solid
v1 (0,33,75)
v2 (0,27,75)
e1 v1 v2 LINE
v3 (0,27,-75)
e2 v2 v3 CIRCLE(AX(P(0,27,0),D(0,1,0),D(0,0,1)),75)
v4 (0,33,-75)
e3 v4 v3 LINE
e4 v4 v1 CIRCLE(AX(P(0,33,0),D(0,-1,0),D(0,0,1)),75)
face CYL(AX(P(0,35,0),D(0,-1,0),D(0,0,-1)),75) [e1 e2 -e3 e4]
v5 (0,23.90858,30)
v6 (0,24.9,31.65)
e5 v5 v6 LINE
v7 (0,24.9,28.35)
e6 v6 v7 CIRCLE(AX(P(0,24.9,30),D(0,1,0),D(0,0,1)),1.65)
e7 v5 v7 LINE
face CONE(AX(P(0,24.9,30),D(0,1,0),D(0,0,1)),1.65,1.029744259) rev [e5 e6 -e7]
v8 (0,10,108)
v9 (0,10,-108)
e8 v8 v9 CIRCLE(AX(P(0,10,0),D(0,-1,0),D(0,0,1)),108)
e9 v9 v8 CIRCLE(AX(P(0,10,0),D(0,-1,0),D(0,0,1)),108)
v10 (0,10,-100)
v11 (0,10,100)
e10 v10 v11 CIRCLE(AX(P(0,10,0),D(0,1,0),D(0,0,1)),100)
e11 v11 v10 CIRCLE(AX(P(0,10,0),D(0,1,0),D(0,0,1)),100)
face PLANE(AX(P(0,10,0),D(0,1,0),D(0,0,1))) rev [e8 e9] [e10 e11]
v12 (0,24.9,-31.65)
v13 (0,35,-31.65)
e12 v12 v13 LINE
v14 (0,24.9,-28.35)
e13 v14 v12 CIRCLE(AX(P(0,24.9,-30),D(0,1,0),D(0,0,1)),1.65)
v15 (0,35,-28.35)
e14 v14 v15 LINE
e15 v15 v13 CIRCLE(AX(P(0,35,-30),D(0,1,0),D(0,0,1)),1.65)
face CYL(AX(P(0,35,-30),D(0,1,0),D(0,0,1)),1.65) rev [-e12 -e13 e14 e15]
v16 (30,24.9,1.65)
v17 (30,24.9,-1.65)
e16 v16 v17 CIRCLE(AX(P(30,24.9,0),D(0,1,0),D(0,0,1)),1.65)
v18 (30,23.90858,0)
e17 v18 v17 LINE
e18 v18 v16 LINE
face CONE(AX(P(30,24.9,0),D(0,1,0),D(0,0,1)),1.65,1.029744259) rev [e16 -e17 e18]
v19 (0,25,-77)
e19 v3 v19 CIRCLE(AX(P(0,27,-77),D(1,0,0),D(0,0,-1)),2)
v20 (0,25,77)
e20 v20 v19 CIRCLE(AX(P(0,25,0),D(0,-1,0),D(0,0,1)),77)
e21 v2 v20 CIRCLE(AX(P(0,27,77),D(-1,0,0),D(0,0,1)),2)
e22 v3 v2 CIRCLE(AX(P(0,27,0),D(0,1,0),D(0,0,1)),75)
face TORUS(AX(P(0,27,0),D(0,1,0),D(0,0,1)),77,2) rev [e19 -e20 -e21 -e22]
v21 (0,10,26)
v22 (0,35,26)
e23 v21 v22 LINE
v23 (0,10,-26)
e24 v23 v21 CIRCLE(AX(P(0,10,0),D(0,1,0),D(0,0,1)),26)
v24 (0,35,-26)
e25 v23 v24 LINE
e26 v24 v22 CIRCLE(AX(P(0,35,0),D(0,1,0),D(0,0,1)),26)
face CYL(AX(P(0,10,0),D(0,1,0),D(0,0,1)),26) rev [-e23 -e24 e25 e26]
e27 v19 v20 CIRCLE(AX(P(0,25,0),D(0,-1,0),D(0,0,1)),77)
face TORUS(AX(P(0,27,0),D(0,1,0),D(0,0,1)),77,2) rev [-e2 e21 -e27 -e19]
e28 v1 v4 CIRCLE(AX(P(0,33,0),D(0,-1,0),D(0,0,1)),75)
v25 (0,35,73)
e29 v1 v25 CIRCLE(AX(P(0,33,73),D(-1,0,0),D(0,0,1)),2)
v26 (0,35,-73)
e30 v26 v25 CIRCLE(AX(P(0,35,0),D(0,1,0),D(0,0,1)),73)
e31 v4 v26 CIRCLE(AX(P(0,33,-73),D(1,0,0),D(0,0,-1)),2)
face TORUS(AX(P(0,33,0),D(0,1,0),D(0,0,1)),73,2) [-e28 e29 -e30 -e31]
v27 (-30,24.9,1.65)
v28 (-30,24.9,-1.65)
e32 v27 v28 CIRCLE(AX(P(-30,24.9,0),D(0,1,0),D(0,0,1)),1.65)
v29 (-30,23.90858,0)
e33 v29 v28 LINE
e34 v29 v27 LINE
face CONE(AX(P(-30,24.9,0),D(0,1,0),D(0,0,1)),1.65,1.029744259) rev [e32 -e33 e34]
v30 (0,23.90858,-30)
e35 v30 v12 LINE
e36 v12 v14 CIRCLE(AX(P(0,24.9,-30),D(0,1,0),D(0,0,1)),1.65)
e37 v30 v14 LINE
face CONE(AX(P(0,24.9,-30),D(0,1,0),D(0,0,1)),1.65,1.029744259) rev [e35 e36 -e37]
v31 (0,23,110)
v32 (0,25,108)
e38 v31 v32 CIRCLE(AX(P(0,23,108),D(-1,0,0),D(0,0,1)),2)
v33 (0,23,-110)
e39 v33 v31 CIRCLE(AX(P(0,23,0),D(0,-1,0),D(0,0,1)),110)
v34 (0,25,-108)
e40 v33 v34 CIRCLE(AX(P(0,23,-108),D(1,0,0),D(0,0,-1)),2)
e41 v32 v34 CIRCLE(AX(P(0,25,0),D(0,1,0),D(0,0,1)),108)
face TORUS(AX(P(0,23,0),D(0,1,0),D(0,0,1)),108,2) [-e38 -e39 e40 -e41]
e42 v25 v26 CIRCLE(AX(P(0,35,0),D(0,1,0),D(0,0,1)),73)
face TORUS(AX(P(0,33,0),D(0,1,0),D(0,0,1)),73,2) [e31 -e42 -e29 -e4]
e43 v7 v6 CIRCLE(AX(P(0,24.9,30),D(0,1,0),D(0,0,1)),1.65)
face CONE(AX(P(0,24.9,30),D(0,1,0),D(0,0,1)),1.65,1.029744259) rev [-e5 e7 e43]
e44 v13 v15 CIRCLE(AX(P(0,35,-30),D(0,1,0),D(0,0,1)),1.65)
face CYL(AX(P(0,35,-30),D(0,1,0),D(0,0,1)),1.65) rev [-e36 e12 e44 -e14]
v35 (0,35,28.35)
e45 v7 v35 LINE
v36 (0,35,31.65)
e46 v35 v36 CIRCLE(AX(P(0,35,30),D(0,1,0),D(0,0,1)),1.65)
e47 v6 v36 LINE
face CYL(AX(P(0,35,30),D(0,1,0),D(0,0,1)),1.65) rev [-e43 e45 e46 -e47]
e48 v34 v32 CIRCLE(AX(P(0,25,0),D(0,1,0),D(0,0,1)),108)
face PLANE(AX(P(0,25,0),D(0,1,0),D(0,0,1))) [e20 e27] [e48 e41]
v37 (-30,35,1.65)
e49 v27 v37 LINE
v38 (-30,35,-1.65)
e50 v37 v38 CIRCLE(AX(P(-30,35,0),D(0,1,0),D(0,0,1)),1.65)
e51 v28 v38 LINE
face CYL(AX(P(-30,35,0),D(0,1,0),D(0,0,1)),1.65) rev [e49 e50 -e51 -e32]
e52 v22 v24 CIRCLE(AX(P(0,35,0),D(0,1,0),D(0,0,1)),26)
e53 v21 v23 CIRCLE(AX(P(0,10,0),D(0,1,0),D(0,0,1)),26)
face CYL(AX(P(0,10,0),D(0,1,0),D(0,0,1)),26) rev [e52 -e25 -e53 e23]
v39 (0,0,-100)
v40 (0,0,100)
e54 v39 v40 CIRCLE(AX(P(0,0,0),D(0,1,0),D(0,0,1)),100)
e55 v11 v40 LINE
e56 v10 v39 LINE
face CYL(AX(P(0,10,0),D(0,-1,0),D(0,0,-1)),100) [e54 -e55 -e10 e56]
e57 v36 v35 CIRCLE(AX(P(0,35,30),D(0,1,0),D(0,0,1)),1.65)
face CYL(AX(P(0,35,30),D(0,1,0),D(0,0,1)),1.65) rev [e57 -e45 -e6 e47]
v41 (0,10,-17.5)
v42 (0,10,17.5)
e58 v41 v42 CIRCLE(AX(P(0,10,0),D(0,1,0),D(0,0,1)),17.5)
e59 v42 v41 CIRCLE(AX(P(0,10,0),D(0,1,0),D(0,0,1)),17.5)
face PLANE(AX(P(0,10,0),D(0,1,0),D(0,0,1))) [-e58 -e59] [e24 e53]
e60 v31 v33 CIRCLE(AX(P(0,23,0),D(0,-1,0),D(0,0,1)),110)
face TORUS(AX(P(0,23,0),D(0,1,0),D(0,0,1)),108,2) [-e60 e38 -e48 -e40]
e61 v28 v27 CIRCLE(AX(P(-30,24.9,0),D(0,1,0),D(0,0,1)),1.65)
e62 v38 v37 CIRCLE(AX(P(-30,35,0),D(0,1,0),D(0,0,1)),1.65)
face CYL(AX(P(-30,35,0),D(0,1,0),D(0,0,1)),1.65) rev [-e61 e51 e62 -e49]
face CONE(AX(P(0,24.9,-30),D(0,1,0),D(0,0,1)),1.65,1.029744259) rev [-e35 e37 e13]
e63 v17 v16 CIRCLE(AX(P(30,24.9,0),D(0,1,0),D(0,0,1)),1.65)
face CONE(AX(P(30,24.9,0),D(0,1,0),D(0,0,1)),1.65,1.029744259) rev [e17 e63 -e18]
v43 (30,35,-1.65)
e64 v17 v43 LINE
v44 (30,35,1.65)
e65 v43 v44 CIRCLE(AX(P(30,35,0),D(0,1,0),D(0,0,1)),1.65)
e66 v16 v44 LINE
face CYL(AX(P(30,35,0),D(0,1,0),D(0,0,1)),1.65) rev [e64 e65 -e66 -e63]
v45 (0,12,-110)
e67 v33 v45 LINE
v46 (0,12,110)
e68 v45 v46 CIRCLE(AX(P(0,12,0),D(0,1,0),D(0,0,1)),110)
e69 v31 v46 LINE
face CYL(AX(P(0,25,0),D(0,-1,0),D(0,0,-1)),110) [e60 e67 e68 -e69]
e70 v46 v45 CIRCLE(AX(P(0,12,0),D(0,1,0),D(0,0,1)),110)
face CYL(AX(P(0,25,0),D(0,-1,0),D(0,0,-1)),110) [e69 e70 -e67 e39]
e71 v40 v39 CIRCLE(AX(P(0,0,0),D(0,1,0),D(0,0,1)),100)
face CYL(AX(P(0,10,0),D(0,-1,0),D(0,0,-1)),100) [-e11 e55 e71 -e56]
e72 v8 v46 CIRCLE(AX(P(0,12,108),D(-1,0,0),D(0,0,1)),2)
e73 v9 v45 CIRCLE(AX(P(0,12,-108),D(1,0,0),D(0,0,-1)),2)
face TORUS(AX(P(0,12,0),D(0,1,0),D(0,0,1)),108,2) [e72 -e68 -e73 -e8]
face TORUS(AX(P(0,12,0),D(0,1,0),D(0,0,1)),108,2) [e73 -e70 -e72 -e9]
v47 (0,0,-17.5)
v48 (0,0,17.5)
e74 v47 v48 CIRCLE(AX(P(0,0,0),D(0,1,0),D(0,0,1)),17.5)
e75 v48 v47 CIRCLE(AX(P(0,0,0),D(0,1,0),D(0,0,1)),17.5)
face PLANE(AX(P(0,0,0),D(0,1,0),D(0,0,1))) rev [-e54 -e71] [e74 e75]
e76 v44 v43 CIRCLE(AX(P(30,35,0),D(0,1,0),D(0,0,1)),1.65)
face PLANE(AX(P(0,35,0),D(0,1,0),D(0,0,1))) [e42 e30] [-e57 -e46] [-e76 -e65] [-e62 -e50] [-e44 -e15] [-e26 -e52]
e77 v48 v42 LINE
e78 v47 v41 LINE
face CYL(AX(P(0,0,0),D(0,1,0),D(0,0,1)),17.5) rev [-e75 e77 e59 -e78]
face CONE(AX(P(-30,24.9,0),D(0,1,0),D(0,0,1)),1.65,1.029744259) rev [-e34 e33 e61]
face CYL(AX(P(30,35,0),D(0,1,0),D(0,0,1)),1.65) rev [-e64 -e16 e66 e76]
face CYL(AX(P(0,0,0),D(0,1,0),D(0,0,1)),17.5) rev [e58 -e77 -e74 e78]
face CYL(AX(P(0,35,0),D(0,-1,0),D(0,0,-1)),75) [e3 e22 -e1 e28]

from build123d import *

# Parameters (mm, degrees)
SKETCH1_R           = 100
BOSS_EXTRUDE1_DEPTH = 10
SKETCH2_R           = 110
BOSS_EXTRUDE2_DEPTH = 15
SKETCH3_R           = 75
BOSS_EXTRUDE3_DEPTH = 10
FILLET1_R           = 2
SKETCH4_R           = 26
CUT_EXTRUDE1_DEPTH  = 25
SKETCH5_R           = 17.5
CUT_EXTRUDE2_DEPTH  = 158.559512566
CIRPATTERN1_COUNT   = 4
FILLET2_R           = 2


with BuildPart() as part:
    # Sketch1 → Boss-Extrude1 (new body)
    with BuildSketch(Plane(origin=(0, 0, 0), x_dir=(1, 0, 0), z_dir=(0, 1, 0))):
        with Locations(Location((0, 0, 0), (0, 0, 270))):
            Circle(SKETCH1_R)
    extrude(amount=BOSS_EXTRUDE1_DEPTH)

    # Sketch2 → Boss-Extrude2 (add)
    with BuildSketch(Plane(origin=(0, 10, 0), x_dir=(1, 0, 0), z_dir=(0, 1, 0))):
        with Locations(Location((0, 0, 0), (0, 0, 270))):
            Circle(SKETCH2_R)
    extrude(amount=BOSS_EXTRUDE2_DEPTH)

    # Sketch3 → Boss-Extrude3 (add)
    with BuildSketch(Plane(origin=(0, 25, 0), x_dir=(1, 0, 0), z_dir=(0, 1, 0))):
        with Locations(Location((0, 0, 0), (0, 0, 270))):
            Circle(SKETCH3_R)
    extrude(amount=BOSS_EXTRUDE3_DEPTH)

    # Fillet1
    fillet1_edges = [part.edges().sort_by_distance(p)[0] for p in [
        (0, 25, -75),
        (0, 35, -75),
    ]]
    fillet(fillet1_edges, radius=FILLET1_R)

    # Sketch4 → Cut-Extrude1 (cut)
    with BuildSketch(Plane(origin=(0, 35, 0), x_dir=(1, 0, 0), z_dir=(0, 1, 0))):
        with Locations(Location((0, 0, 0), (0, 0, 270))):
            Circle(SKETCH4_R)
    extrude(amount=-CUT_EXTRUDE1_DEPTH, mode=Mode.SUBTRACT)

    # Sketch5 → Cut-Extrude2 (cut, through all)
    with BuildSketch(Plane(origin=(0, 10, 0), x_dir=(1, 0, 0), z_dir=(0, 1, 0))):
        with Locations(Location((0, 0, 0), (0, 0, 270))):
            Circle(SKETCH5_R)
    extrude(amount=-CUT_EXTRUDE2_DEPTH, mode=Mode.SUBTRACT)

    # Sketch8 → M4 Tapped Hole1 (revolve, cut)
    with BuildSketch(Plane(origin=(0, 35, -30), x_dir=(0, 0, 1), z_dir=(1, 0, 0))):
        Polygon((0, 0), (0, 11.091420021), (1.65, 10.1), (1.65, 0), align=None)
    m4_tapped_hole1 = revolve(axis=Axis((0, 41.35, -30), (0, -1, 0)), mode=Mode.SUBTRACT)

    # CirPattern1: M4 Tapped Hole1 ×4 about axis
    cirpattern1_axis = Axis((0, 0, 0), (0, 1, 0))
    for i in range(1, CIRPATTERN1_COUNT):
        add(m4_tapped_hole1.rotate(cirpattern1_axis, i * 360 / CIRPATTERN1_COUNT), mode=Mode.SUBTRACT)

    # Fillet2
    fillet2_edges = [part.edges().sort_by_distance(p)[0] for p in [
        (0, 10, -110),
        (0, 25, -110),
    ]]
    fillet(fillet2_edges, radius=FILLET2_R)


solid = part.part
